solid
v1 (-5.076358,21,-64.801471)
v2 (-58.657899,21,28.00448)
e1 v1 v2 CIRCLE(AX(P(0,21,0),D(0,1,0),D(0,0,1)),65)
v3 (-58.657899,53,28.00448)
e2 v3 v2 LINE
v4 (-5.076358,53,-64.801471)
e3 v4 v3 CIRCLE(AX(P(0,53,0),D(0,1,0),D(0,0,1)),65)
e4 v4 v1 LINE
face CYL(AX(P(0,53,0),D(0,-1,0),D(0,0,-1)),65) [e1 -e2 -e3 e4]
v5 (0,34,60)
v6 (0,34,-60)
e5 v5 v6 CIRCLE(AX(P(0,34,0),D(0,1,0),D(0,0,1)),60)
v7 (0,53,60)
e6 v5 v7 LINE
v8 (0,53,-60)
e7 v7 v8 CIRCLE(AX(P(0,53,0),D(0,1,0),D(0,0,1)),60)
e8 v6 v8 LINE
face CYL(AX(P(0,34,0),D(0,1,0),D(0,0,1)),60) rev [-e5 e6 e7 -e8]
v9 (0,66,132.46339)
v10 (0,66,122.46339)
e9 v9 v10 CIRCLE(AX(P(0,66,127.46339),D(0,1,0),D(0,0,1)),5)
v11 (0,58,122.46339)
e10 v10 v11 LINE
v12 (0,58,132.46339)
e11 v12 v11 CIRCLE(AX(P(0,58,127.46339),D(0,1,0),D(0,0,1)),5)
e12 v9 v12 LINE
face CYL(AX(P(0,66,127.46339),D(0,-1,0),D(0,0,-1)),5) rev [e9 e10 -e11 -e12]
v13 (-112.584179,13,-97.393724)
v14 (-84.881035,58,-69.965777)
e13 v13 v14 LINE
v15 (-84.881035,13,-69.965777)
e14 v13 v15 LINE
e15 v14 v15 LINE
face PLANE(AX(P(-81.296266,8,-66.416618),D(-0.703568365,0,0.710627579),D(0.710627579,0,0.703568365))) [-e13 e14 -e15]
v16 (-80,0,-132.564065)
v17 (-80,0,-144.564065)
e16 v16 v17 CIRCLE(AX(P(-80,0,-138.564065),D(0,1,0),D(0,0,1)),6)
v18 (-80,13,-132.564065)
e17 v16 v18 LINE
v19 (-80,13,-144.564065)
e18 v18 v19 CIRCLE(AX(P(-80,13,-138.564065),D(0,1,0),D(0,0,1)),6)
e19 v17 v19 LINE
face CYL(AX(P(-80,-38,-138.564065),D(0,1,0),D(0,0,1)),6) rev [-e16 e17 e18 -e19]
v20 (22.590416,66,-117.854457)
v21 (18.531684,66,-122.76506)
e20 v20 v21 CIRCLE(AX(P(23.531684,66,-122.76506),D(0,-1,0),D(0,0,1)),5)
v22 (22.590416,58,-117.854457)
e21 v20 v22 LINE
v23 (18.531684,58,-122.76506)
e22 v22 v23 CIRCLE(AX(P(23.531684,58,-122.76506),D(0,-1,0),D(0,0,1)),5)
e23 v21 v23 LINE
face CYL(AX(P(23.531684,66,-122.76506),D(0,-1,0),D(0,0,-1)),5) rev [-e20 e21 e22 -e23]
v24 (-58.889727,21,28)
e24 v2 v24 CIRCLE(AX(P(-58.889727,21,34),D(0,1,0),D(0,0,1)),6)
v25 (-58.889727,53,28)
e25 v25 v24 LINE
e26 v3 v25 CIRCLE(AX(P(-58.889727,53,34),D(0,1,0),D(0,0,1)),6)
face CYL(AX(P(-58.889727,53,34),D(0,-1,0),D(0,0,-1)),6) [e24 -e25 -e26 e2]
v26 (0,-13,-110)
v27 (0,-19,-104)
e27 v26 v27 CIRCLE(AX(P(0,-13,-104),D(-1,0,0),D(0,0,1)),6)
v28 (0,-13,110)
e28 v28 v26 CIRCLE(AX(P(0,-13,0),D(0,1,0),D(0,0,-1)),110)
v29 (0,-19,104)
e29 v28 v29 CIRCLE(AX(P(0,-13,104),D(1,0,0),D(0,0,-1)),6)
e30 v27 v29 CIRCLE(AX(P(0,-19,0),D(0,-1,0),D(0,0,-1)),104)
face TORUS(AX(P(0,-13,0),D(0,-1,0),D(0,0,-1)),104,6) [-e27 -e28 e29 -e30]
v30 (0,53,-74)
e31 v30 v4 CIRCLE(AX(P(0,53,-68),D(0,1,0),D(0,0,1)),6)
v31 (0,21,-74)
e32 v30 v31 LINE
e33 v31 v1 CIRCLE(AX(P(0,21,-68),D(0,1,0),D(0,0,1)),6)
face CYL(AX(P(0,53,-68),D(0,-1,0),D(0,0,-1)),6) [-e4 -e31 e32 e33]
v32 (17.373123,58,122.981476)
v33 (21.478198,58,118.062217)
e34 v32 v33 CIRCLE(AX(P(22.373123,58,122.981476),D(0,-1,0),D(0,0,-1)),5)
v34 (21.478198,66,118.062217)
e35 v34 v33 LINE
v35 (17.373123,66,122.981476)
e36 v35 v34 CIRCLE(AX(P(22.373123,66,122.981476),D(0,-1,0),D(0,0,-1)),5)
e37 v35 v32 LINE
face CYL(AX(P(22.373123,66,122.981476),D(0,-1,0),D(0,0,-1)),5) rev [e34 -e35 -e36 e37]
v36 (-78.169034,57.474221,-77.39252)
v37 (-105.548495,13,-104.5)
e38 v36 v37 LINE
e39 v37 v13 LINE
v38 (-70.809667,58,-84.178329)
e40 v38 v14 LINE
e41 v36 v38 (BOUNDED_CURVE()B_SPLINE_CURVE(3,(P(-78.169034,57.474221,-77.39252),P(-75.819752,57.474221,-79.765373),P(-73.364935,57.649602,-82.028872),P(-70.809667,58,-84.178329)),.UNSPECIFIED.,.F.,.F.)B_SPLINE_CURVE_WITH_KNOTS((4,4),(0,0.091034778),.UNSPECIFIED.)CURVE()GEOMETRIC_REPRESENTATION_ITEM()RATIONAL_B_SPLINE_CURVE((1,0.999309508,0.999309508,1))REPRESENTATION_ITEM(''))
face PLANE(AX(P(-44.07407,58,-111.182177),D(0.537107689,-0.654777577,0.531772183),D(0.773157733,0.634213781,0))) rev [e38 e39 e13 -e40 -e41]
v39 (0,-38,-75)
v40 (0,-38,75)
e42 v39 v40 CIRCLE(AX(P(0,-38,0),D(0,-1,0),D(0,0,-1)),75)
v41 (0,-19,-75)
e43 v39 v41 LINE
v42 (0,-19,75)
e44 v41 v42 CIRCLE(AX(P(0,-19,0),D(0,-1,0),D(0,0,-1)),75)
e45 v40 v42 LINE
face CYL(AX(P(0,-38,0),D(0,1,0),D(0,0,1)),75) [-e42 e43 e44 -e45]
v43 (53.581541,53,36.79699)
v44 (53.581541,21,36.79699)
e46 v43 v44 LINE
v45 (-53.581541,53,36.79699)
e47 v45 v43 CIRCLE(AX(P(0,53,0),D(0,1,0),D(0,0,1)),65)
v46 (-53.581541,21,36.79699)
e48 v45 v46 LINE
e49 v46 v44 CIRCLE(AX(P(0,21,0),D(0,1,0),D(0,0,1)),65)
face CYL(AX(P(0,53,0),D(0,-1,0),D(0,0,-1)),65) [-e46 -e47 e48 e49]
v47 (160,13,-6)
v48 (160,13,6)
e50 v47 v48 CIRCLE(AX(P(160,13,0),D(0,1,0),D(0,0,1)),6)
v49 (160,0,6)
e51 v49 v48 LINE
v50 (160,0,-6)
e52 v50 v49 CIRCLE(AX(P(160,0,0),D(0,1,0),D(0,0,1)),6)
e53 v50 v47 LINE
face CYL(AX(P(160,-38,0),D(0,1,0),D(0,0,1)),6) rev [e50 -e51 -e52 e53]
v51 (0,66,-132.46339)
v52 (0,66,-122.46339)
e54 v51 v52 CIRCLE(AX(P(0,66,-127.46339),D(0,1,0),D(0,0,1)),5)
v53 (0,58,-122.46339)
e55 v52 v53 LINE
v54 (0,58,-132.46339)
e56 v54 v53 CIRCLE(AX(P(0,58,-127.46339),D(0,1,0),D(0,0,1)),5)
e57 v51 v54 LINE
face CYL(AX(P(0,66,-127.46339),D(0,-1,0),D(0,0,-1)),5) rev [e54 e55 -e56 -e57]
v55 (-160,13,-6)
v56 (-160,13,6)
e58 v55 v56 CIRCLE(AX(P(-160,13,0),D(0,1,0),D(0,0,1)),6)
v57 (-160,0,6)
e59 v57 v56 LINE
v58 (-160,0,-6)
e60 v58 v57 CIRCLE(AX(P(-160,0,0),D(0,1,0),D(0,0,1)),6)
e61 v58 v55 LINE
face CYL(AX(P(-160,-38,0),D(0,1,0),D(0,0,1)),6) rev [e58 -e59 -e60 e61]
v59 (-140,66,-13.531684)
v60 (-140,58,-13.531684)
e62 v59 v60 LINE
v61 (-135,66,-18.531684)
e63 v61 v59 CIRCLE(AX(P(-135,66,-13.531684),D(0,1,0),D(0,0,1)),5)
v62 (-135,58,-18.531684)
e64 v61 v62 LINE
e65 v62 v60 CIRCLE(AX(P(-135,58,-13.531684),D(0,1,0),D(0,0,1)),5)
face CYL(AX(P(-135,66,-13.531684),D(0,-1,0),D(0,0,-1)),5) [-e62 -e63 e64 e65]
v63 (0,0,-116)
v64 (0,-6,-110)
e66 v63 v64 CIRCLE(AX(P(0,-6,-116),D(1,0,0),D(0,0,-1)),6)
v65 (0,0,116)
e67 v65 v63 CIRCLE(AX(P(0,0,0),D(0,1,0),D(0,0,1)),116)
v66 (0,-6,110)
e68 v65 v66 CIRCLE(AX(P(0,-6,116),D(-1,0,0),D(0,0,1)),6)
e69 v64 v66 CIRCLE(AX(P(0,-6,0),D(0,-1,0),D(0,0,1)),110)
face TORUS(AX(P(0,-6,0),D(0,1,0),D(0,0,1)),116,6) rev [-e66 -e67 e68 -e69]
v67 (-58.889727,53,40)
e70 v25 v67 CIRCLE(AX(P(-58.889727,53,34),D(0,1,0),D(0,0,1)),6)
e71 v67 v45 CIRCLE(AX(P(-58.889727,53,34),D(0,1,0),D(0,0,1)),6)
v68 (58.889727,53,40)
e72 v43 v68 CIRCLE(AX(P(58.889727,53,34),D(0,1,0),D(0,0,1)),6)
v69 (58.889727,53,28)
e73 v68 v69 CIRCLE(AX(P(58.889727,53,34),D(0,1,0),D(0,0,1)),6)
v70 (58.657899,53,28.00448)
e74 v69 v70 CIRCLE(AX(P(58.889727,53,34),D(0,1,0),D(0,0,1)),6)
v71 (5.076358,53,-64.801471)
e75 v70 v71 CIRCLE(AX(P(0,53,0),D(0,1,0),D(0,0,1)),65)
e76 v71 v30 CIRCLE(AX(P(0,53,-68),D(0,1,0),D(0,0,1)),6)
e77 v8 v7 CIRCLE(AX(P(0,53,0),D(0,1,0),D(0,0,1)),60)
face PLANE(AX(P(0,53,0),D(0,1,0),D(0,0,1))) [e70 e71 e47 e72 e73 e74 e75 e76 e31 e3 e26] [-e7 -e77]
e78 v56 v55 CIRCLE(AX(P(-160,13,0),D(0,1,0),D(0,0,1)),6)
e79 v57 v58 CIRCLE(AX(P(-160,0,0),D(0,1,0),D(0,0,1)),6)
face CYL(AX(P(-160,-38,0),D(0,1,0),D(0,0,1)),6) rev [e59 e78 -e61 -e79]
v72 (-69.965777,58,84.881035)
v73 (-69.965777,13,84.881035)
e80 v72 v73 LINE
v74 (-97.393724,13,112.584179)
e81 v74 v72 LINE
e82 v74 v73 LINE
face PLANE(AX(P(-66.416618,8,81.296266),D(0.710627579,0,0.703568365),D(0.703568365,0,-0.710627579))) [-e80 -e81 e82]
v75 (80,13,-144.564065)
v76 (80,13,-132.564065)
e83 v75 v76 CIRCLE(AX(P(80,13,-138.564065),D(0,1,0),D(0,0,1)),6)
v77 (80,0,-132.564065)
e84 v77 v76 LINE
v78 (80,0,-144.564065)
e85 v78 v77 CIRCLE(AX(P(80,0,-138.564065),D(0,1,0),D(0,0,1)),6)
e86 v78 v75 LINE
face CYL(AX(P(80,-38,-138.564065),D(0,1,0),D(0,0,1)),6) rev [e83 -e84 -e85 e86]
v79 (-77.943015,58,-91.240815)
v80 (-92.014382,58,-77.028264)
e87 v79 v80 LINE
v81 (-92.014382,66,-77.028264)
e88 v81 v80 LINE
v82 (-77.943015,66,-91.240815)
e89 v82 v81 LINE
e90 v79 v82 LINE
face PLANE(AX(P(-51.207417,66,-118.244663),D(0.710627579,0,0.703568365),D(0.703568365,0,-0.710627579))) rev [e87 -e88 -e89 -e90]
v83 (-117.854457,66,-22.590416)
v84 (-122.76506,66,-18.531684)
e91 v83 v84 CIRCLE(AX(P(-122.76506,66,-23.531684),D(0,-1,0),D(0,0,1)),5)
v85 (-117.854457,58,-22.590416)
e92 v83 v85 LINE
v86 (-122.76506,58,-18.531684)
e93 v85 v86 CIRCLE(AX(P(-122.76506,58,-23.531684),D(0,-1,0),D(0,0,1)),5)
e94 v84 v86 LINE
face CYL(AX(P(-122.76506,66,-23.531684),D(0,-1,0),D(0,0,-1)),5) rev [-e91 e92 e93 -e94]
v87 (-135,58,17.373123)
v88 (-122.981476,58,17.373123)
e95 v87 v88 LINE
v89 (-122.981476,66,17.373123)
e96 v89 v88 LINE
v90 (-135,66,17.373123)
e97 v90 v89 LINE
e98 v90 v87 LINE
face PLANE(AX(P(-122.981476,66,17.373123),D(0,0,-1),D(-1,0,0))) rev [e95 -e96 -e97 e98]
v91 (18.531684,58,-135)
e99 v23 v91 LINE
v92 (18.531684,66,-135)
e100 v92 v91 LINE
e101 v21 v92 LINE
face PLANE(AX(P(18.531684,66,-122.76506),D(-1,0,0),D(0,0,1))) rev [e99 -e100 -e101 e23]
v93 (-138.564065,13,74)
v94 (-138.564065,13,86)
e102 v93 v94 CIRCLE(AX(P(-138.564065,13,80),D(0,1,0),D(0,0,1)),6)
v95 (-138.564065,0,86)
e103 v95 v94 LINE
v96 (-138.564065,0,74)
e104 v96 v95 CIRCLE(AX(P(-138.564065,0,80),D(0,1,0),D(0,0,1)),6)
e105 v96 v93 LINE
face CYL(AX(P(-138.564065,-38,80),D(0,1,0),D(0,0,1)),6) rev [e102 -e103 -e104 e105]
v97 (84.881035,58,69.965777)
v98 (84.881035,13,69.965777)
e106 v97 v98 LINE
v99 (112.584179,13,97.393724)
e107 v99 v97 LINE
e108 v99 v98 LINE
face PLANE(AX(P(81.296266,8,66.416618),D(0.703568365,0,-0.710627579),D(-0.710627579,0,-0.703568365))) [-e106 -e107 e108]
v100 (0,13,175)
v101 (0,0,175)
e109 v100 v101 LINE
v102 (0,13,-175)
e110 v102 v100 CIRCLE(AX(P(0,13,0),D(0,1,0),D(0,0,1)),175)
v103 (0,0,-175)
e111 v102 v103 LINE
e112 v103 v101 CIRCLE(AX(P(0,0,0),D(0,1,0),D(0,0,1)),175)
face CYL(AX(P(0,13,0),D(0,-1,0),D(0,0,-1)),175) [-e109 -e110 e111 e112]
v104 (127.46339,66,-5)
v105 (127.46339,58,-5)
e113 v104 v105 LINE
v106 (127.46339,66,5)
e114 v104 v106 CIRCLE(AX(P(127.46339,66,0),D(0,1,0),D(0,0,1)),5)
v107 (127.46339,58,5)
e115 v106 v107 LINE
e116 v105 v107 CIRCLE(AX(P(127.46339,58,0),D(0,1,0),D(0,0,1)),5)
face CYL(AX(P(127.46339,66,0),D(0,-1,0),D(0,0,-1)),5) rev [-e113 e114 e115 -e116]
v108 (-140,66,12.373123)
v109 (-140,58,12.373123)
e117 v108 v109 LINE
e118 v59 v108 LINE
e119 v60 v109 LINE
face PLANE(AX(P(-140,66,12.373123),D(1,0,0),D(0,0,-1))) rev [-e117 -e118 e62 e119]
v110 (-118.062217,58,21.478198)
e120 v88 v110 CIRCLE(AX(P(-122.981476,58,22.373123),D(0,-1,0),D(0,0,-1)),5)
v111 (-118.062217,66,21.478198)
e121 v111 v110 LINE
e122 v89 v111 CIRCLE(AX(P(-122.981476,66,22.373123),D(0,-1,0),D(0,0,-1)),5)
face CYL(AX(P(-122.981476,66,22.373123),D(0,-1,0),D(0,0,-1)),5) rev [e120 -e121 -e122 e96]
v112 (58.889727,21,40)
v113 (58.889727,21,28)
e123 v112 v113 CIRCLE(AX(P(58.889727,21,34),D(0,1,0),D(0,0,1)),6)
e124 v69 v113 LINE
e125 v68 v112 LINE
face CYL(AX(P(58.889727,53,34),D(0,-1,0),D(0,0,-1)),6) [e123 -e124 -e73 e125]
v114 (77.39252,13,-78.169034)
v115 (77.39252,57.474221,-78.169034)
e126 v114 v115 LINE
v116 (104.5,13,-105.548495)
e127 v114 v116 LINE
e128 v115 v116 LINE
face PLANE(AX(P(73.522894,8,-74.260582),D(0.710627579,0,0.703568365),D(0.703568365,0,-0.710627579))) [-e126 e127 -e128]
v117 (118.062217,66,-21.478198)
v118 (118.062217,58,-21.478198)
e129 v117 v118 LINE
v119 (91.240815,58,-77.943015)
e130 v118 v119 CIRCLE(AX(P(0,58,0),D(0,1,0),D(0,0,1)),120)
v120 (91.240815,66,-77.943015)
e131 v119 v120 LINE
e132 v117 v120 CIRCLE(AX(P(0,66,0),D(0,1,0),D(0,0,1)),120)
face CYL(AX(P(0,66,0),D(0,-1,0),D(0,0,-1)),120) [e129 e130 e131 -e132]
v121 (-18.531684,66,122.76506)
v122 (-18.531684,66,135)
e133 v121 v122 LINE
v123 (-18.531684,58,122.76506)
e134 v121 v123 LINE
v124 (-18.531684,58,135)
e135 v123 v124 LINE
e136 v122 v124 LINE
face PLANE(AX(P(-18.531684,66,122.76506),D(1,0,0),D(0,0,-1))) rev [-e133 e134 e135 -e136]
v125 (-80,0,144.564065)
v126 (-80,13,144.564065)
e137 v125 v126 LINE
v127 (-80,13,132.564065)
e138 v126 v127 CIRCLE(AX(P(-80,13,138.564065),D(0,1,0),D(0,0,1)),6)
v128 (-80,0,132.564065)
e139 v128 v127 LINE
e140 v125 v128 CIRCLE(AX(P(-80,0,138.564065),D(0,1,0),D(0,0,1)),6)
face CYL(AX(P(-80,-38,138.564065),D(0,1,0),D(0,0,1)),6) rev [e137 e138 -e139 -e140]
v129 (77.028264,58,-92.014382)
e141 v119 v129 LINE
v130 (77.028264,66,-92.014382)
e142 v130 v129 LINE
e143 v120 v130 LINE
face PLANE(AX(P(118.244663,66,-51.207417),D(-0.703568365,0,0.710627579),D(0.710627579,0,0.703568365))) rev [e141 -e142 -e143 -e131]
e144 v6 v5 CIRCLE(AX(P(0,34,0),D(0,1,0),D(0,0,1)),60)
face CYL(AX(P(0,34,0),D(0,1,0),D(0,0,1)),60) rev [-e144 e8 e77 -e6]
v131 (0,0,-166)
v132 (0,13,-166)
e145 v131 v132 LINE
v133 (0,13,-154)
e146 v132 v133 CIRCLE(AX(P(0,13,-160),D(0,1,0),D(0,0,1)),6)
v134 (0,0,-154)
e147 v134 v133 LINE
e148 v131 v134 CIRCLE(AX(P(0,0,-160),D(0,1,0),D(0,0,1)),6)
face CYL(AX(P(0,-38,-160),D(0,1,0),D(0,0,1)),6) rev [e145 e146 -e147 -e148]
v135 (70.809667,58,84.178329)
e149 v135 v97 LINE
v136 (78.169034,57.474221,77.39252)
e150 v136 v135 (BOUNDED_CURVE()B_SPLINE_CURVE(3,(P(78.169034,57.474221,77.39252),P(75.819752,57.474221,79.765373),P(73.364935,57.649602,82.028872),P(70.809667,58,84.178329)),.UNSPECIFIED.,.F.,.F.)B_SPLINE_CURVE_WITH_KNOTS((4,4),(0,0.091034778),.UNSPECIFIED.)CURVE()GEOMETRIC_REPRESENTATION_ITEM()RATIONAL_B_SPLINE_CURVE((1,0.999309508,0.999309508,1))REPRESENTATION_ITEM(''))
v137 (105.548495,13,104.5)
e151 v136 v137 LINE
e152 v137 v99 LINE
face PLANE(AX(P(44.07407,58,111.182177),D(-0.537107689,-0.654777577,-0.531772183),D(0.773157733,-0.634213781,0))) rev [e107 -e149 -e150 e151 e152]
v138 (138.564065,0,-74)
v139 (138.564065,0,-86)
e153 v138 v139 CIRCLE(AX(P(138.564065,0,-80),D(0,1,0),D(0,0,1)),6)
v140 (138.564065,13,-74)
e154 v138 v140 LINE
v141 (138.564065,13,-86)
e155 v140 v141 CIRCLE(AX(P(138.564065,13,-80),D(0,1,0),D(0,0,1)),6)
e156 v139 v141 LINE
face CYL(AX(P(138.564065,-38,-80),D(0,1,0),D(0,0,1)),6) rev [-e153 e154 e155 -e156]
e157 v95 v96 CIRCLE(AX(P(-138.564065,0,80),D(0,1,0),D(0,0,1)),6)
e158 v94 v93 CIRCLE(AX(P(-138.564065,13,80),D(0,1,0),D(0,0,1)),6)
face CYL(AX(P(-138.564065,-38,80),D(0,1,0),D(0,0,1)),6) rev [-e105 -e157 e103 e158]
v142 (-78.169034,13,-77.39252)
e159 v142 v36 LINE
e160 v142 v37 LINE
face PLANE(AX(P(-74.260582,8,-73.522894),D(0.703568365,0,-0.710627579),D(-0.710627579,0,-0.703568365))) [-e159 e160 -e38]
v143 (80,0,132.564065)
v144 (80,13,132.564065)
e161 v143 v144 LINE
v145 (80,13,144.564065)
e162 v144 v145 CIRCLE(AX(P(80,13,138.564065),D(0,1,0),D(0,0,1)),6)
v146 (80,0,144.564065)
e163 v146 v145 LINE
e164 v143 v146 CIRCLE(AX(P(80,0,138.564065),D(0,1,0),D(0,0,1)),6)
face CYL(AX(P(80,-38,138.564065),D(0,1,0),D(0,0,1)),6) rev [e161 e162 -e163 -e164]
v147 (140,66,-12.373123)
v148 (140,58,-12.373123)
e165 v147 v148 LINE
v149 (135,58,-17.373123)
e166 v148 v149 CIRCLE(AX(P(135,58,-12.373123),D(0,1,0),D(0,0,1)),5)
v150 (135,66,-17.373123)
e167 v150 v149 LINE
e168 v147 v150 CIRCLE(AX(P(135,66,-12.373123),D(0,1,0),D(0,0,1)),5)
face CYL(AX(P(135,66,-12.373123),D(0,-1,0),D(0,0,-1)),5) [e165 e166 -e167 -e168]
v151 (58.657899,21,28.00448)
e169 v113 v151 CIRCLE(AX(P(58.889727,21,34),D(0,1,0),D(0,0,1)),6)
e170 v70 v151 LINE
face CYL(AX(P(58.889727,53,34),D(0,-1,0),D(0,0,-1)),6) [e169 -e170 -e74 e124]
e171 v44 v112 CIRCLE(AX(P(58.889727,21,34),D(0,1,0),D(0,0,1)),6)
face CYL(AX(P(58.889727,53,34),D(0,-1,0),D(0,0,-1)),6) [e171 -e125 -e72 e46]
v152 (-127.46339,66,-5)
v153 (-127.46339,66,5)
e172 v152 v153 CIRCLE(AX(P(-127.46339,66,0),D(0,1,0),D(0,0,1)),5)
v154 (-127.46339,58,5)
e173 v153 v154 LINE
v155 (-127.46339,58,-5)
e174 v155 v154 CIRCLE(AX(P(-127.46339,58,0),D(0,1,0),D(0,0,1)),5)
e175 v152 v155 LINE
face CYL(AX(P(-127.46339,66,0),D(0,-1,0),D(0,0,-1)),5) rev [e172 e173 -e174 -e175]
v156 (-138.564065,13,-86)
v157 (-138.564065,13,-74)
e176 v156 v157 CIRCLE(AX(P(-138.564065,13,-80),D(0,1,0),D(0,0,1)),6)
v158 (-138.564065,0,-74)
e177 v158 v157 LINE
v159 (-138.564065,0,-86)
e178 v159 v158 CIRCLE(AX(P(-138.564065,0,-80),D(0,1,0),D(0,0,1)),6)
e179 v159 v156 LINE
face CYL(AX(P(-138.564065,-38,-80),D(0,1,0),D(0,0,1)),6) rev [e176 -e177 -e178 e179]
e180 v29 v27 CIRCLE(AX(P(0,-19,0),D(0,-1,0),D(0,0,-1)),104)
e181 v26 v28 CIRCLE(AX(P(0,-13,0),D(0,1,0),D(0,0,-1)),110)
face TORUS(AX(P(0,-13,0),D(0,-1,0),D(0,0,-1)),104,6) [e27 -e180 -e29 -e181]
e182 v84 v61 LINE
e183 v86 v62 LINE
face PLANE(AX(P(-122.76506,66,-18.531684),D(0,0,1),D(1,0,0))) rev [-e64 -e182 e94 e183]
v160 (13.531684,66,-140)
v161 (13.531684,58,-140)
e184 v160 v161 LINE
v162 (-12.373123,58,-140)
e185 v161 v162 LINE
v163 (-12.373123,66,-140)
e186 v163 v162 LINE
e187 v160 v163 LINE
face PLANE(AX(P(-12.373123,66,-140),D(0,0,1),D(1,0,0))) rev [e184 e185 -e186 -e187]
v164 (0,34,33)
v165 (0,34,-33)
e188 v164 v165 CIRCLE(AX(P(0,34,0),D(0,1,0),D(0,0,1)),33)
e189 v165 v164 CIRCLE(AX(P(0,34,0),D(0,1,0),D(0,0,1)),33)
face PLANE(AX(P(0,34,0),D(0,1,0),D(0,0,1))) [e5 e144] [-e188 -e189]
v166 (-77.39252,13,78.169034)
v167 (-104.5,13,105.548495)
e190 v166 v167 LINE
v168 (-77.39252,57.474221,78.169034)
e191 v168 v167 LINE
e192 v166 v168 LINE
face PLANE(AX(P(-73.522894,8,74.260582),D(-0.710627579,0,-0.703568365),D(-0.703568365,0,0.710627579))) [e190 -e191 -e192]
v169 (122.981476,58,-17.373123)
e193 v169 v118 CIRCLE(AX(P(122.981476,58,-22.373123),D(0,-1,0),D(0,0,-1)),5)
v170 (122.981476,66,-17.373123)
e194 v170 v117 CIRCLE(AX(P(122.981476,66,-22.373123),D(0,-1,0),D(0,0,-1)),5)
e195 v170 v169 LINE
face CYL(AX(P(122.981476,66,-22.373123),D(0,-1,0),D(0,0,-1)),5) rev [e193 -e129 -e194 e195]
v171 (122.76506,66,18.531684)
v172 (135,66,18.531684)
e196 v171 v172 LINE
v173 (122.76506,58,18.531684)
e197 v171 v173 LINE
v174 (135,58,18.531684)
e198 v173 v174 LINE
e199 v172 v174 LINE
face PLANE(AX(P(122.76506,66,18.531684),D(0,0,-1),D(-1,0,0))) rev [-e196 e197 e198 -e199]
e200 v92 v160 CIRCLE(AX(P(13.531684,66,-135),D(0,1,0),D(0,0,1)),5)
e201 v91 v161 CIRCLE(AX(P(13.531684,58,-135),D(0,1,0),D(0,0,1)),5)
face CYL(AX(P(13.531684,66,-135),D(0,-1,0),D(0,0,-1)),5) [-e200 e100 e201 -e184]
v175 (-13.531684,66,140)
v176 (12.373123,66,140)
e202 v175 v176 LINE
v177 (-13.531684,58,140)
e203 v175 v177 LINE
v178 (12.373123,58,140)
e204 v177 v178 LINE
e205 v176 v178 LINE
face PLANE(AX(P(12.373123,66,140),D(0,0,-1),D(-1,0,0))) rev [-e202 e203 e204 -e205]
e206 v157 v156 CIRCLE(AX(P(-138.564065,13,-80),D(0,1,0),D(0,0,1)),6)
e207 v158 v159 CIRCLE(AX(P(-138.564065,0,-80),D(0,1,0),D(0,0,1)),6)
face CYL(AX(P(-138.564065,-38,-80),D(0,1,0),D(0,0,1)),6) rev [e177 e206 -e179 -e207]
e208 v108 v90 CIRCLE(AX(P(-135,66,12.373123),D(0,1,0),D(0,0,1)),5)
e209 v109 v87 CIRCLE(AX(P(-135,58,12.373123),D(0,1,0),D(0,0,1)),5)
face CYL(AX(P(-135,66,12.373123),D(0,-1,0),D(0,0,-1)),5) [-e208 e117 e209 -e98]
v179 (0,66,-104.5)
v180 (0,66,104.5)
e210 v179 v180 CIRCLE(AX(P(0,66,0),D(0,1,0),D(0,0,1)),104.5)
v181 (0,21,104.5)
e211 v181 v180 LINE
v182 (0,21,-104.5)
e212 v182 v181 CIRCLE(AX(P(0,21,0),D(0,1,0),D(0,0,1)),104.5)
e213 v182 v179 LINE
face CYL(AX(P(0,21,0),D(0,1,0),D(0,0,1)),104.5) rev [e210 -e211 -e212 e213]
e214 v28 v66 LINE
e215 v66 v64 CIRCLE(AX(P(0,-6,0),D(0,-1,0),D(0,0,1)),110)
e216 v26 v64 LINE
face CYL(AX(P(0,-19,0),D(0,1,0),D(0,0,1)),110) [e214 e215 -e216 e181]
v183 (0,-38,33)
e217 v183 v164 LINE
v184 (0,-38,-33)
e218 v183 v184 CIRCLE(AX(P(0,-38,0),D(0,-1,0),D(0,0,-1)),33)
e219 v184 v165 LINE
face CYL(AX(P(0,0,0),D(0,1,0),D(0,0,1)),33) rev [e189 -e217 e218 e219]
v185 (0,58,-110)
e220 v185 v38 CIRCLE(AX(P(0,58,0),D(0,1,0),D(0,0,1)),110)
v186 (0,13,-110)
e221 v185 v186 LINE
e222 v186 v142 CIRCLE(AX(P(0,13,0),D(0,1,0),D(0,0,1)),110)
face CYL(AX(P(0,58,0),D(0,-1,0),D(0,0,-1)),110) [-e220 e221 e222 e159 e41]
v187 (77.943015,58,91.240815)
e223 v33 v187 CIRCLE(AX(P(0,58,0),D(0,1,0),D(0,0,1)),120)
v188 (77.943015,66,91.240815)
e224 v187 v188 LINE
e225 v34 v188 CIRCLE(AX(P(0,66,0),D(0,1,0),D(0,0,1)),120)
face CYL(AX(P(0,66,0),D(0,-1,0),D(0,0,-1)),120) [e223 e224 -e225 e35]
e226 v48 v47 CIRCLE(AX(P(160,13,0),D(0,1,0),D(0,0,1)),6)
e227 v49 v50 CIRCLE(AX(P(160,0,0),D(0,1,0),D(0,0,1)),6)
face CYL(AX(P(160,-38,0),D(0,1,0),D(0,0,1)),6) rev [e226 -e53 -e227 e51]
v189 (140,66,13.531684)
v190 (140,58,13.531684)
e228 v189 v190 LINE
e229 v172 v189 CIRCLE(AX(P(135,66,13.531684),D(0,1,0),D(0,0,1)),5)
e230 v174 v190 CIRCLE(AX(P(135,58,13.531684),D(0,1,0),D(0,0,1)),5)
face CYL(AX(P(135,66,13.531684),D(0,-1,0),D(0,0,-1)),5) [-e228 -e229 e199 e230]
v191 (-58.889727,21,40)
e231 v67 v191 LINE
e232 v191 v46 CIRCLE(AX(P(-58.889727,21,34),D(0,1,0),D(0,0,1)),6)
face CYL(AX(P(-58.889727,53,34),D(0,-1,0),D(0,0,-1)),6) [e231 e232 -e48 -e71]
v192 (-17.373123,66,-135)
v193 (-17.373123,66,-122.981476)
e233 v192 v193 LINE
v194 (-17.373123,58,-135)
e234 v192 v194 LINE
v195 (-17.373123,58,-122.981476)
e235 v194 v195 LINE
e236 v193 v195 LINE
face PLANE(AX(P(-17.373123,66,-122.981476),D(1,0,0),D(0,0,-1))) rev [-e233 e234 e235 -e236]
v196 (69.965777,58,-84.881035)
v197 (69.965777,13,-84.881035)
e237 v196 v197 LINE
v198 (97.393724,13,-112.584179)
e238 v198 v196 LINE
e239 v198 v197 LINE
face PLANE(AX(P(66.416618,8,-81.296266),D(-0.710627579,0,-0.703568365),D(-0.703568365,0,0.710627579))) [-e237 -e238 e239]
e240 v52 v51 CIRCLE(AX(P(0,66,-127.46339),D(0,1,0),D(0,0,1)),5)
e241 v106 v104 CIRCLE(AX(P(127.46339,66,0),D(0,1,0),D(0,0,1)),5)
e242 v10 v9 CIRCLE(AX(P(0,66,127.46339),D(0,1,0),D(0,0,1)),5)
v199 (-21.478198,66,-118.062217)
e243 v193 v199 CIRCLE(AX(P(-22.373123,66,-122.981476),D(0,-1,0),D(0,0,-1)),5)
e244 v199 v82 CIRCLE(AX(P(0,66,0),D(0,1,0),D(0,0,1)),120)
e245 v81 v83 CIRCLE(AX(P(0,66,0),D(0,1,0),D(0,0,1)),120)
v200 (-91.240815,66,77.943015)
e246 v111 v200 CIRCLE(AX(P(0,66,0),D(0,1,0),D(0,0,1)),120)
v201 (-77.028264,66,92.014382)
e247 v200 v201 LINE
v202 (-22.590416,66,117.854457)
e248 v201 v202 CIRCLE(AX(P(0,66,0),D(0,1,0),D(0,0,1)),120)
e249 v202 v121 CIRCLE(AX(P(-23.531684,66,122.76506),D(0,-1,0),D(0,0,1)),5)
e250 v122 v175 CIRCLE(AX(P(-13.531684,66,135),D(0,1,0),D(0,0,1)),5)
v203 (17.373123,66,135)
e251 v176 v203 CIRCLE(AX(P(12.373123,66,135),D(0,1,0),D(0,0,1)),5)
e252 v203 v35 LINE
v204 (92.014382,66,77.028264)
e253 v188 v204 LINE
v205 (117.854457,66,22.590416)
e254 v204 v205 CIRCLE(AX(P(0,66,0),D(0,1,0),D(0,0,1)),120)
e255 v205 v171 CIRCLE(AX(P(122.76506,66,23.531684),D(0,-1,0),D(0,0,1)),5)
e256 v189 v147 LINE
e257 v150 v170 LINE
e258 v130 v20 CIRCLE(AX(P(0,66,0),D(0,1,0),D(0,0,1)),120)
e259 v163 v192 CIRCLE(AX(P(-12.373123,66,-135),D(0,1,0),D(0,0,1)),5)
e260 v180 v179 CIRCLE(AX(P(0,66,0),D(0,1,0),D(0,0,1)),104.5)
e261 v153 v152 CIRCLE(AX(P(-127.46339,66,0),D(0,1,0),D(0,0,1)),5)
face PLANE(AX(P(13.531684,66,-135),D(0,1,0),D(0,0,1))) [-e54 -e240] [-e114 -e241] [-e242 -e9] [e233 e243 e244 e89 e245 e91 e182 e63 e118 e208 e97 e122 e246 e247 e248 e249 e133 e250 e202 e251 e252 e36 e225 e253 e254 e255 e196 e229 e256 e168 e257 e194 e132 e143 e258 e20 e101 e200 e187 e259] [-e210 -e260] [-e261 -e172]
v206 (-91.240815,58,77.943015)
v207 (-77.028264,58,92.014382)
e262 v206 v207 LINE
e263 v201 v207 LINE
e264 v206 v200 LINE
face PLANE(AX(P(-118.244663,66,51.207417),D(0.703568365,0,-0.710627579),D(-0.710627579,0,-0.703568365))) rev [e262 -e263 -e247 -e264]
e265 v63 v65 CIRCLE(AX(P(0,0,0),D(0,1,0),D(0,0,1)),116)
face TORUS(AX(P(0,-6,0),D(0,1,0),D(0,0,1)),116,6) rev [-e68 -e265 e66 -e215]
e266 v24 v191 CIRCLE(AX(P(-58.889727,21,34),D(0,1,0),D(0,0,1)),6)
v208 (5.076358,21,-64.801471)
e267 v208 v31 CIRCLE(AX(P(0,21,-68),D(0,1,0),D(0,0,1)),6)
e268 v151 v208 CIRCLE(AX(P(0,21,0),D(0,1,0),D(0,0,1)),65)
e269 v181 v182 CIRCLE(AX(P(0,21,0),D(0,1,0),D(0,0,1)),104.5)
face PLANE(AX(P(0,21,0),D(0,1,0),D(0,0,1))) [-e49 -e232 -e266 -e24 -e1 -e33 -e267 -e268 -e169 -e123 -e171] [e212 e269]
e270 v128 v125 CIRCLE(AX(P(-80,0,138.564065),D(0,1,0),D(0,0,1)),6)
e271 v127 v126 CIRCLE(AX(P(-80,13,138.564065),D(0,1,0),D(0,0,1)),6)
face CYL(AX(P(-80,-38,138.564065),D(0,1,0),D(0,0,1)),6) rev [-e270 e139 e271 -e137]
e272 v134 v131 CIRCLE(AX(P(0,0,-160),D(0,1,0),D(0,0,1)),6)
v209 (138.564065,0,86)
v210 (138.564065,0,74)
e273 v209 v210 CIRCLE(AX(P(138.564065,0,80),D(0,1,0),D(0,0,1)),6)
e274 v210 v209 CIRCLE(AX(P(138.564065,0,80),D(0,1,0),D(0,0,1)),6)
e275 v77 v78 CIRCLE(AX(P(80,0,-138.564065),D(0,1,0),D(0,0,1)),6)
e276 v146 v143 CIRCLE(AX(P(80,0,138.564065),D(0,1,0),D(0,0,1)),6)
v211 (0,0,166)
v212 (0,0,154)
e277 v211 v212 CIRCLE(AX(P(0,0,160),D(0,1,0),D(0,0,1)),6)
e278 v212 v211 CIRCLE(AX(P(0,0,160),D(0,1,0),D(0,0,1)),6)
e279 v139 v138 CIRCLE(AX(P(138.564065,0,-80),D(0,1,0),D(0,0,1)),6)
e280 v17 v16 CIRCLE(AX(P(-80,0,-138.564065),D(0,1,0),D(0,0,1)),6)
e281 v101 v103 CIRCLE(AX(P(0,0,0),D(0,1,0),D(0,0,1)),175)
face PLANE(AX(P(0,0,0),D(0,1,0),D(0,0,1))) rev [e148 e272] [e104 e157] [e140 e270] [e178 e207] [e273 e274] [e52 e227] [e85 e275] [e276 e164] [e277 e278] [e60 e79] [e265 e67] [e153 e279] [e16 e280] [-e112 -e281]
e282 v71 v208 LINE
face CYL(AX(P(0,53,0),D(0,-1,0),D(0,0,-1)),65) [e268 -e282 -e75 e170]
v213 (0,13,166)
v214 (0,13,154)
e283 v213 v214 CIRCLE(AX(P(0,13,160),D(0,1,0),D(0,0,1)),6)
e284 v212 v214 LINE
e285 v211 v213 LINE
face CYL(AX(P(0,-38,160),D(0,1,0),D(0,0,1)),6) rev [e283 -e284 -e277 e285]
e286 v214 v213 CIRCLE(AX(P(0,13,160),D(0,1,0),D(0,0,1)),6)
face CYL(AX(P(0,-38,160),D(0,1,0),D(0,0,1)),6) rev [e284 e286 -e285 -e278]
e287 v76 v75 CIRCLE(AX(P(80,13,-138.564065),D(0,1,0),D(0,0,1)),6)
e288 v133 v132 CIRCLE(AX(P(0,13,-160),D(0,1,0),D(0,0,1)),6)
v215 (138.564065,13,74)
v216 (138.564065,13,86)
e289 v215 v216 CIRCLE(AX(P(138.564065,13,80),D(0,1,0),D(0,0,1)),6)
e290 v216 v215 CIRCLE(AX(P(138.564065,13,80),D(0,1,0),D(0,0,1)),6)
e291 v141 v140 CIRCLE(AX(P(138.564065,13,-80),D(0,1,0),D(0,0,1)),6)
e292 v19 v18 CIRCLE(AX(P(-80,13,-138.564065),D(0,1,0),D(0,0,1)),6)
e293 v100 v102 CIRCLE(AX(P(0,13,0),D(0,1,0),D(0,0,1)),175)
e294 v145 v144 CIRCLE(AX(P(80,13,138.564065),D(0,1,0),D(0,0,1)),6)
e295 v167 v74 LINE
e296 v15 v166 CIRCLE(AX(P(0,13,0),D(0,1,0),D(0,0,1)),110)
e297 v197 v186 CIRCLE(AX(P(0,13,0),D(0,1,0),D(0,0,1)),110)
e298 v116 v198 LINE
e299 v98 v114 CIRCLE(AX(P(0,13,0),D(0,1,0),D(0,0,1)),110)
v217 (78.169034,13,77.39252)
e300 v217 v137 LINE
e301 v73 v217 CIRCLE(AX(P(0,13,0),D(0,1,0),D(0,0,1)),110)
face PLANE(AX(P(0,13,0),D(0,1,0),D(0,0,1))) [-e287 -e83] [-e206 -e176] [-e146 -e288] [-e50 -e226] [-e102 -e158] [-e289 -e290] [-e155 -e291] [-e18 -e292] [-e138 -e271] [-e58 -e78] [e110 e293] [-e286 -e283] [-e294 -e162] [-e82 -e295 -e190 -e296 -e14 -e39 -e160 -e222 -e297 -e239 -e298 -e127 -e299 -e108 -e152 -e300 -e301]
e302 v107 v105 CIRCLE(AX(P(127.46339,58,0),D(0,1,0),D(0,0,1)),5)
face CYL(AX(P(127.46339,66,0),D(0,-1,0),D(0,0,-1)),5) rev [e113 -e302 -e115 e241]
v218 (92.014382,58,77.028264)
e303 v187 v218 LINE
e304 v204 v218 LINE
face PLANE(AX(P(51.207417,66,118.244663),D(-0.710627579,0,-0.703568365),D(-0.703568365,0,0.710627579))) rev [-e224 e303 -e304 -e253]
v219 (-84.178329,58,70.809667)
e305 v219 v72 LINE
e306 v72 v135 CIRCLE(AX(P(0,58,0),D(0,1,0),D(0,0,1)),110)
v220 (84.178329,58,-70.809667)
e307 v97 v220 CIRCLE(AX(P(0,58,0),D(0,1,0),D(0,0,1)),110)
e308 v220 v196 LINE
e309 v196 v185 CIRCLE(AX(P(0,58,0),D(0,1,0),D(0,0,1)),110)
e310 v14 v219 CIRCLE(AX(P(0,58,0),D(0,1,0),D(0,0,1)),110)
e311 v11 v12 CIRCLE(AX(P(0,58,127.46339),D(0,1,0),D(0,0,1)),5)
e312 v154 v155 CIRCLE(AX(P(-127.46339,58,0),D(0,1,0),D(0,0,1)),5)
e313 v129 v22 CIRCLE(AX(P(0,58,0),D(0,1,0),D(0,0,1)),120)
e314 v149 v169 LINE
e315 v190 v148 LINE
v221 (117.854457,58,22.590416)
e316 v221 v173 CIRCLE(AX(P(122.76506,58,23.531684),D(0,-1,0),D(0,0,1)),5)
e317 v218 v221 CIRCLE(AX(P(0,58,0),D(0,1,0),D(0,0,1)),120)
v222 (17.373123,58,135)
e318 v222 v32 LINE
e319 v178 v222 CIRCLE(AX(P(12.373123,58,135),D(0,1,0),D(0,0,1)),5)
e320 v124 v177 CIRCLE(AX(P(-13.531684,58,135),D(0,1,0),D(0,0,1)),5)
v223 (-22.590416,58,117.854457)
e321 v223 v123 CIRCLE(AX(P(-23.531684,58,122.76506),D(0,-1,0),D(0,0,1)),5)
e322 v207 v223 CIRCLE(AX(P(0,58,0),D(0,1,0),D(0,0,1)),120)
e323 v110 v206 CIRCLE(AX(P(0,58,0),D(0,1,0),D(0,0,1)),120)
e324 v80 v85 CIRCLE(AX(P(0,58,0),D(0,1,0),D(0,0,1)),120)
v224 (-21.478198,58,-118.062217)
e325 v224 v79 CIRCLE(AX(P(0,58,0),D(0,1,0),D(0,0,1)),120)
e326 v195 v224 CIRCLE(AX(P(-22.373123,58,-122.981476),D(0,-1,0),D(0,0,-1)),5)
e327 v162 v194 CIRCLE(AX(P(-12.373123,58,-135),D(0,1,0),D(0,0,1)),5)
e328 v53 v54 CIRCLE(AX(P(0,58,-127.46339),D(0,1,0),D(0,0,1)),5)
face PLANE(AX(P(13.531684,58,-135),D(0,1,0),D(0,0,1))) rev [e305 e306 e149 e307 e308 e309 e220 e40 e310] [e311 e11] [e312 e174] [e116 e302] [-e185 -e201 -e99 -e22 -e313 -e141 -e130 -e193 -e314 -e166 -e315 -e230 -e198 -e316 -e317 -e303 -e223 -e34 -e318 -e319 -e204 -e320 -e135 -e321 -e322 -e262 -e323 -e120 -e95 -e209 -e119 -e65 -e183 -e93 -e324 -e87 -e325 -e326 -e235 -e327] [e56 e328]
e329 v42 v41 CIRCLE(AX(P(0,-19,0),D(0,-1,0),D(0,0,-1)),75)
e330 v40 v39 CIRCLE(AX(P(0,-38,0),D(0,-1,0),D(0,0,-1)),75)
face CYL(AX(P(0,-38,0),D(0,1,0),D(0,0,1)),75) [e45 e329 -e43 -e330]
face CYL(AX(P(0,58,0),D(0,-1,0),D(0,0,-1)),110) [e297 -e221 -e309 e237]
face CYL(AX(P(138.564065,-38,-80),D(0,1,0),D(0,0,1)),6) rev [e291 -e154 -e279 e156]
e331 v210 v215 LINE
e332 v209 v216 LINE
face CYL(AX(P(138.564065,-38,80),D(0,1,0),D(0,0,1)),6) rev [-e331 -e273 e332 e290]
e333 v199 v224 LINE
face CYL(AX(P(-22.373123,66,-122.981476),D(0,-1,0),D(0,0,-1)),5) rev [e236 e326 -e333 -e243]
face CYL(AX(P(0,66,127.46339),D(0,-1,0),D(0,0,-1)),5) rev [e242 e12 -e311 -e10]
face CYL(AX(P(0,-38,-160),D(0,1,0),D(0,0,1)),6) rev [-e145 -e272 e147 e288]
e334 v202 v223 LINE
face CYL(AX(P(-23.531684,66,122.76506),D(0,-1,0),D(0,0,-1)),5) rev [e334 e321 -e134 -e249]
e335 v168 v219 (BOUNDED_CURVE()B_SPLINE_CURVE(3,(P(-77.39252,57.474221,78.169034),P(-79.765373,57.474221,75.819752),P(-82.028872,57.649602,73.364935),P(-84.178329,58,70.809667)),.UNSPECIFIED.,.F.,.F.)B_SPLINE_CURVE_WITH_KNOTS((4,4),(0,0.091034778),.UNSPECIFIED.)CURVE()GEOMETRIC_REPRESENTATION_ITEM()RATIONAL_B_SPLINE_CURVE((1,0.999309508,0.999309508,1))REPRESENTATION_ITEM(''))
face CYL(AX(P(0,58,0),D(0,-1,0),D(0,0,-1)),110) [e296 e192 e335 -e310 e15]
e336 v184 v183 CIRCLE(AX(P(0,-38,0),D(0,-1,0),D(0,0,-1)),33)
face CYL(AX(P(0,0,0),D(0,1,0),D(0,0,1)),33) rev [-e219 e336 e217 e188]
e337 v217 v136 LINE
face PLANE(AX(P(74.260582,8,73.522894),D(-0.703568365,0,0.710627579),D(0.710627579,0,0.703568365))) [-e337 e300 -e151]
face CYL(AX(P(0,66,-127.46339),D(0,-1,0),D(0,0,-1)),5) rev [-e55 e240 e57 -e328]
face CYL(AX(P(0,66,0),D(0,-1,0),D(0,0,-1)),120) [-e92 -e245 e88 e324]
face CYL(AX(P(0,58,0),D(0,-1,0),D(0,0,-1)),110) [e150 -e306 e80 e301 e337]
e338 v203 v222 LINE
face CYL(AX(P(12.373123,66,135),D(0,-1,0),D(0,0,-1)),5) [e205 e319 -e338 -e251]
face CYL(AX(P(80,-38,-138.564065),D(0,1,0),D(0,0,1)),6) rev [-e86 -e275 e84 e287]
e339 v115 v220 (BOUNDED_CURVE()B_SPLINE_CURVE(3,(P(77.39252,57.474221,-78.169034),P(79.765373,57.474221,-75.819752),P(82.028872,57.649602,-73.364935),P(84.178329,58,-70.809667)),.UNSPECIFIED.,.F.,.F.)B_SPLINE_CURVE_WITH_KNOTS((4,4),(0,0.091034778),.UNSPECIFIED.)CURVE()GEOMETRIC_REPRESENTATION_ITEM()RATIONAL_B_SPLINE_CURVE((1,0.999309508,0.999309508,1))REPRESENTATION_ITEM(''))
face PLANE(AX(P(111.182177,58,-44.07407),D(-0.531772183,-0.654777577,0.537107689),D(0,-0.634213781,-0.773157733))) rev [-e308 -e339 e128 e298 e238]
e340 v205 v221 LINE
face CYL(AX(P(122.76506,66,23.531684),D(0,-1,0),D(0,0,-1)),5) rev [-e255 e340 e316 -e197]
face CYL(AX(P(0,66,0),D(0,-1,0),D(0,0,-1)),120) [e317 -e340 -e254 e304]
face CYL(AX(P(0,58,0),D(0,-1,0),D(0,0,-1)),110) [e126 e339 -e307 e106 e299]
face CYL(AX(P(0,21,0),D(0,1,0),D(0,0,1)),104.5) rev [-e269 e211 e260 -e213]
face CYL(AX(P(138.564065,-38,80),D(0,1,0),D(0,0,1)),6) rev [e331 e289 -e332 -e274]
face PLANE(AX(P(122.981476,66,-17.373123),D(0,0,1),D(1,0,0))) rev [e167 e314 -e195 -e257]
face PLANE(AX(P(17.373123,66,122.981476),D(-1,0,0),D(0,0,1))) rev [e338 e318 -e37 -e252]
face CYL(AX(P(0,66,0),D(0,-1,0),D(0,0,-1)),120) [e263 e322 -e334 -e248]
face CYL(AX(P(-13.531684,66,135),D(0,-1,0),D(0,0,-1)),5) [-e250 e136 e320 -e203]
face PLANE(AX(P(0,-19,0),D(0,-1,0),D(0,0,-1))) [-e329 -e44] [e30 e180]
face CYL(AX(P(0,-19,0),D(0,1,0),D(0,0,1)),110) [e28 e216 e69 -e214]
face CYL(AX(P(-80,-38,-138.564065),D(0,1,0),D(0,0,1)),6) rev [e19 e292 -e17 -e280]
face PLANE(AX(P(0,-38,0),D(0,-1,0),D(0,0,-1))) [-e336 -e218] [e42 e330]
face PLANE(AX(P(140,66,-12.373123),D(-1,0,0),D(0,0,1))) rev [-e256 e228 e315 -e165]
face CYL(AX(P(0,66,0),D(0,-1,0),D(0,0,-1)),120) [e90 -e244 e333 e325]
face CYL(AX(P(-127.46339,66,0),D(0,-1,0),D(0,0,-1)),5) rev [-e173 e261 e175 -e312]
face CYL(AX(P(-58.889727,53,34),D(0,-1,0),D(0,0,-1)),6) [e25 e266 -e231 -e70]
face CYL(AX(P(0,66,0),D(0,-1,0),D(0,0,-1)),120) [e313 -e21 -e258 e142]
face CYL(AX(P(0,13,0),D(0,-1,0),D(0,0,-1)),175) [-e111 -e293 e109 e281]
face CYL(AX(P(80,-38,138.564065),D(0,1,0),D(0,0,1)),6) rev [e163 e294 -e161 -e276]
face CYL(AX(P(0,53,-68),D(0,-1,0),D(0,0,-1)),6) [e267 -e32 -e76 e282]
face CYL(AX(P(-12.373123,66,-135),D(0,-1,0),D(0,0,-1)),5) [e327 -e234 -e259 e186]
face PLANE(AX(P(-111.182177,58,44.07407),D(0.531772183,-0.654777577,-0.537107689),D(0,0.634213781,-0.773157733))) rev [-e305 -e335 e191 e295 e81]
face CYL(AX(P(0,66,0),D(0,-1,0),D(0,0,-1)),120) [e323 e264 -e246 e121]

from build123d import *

# Parameters (mm, degrees)
FLANGE_SKETCH_R                = 175
FLANGE_350X13_DEPTH            = 13
HUB_SKETCH_R                   = 110
HUB_220_DEPTH                  = 45
LUG_PLATE_SKETCH_R             = 5
MOUNTING_LUG_PLATE_DEPTH       = 8
HUB_BORE_SKETCH_R              = 104.5
HUB_BORE_209_DEPTH             = 45
BEARING_HOUSING_130_DEPTH      = 32
BEARING_SEAT_SKETCH_R          = 60
BEARING_SEAT_120_DEPTH         = 19
SHAFT_HOLE_SKETCH_R            = 33
SHAFT_HOLE_66_DEPTH            = 250.811929259
REAR_START                     = 19
REAR_BOSS_SKETCH_R             = 110
REAR_BOSS_220_DEPTH            = 19
REAR_STEP_SKETCH_R             = 75
REAR_STEP_150_DEPTH            = 19
REAR_SHAFT_HOLE_SKETCH_R       = 33
REAR_SHAFT_HOLE_66_DEPTH       = 269.451112868
FLANGE_BOLT_HOLES_SKETCH_R     = 6
FLANGE_BOLT_HOLES_12X_12_DEPTH = 254.09879494
REAR_BOSS_FILLET_R6_R          = 6
GUSSET_RIBS_4X_DEPTH           = 58
RIB_TRIM_CUT_1_DEPTH           = 58
RIB_TRIM_CUT_2_DEPTH           = 58
RIB_TRIM_CUT_3_DEPTH           = 58
RIB_TRIM_CUT_4_DEPTH           = 58


with BuildPart() as part:
    # Flange Sketch → Flange Ø350x13 (new body)
    with BuildSketch(Plane(origin=(0, 0, 0), x_dir=(1, 0, 0), z_dir=(0, 1, 0))):
        with Locations(Location((0, 0, 0), (0, 0, 90))):
            Circle(FLANGE_SKETCH_R)
    extrude(amount=FLANGE_350X13_DEPTH)

    # Hub Sketch → Hub Ø220 (add)
    with BuildSketch(Plane(origin=(0, 13, 0), x_dir=(1, 0, 0), z_dir=(0, 1, 0))):
        with Locations(Location((0, 0, 0), (0, 0, 90))):
            Circle(HUB_SKETCH_R)
    extrude(amount=HUB_220_DEPTH)

    # Lug Plate Sketch → Mounting Lug Plate (add)
    with BuildSketch(Plane(origin=(0, 58, 0), x_dir=(1, 0, 0), z_dir=(0, 1, 0))):
        with BuildLine():
            Line((122.981475637, 17.37312339), (135, 17.37312339))
            ThreePointArc((135, 17.37312339), (138.535533906, 15.908657296), (140, 12.37312339))
            Line((140, 12.37312339), (140, -13.53168384))
            ThreePointArc((140, -13.53168384), (138.535533906, -17.067217746), (135, -18.53168384))
            Line((135, -18.53168384), (122.765059588, -18.53168384))
            ThreePointArc((122.765059588, -18.53168384), (119.579650412, -19.677702991), (117.854457205, -22.590416486))
            ThreePointArc((117.854457205, -22.590416486), (84.451840643, -85.251900929), (21.478198454, -118.062216611))
            ThreePointArc((21.478198454, -118.062216611), (18.534202664, -119.777932651), (17.37312339, -122.981475637))
            Line((17.37312339, -122.981475637), (17.37312339, -135))
            ThreePointArc((17.37312339, -135), (15.908657296, -138.535533906), (12.37312339, -140))
            Line((12.37312339, -140), (-13.53168384, -140))
            ThreePointArc((-13.53168384, -140), (-17.067217746, -138.535533906), (-18.53168384, -135))
            Line((-18.53168384, -135), (-18.53168384, -122.765059588))
            ThreePointArc((-18.53168384, -122.765059588), (-19.677702991, -119.579650412), (-22.590416486, -117.854457205))
            ThreePointArc((-22.590416486, -117.854457205), (-85.251900929, -84.451840643), (-118.062216611, -21.478198454))
            ThreePointArc((-118.062216611, -21.478198454), (-119.777932651, -18.534202664), (-122.981475637, -17.37312339))
            Line((-122.981475637, -17.37312339), (-135, -17.37312339))
            ThreePointArc((-135, -17.37312339), (-138.535533906, -15.908657296), (-140, -12.37312339))
            Line((-140, -12.37312339), (-140, 13.53168384))
            ThreePointArc((-140, 13.53168384), (-138.535533906, 17.067217746), (-135, 18.53168384))
            Line((-135, 18.53168384), (-122.765059588, 18.53168384))
            ThreePointArc((-122.765059588, 18.53168384), (-119.579650412, 19.677702991), (-117.854457205, 22.590416486))
            ThreePointArc((-117.854457205, 22.590416486), (-84.451840643, 85.251900929), (-21.478198454, 118.062216611))
            ThreePointArc((-21.478198454, 118.062216611), (-18.534202664, 119.777932651), (-17.37312339, 122.981475637))
            Line((-17.37312339, 122.981475637), (-17.37312339, 135))
            ThreePointArc((-17.37312339, 135), (-15.908657296, 138.535533906), (-12.37312339, 140))
            Line((-12.37312339, 140), (13.53168384, 140))
            ThreePointArc((13.53168384, 140), (17.067217746, 138.535533906), (18.53168384, 135))
            Line((18.53168384, 135), (18.53168384, 122.765059588))
            ThreePointArc((18.53168384, 122.765059588), (19.677702991, 119.579650412), (22.590416486, 117.854457205))
            ThreePointArc((22.590416486, 117.854457205), (85.251900929, 84.451840643), (118.062216611, 21.478198454))
            ThreePointArc((118.062216611, 21.478198454), (119.777932651, 18.534202664), (122.981475637, 17.37312339))
        make_face()
        with Locations(Location((0, 127.463390021, 0), (0, 0, 270))):
            Circle(LUG_PLATE_SKETCH_R, mode=Mode.SUBTRACT)
        with Locations(Location((127.463390021, 0, 0), (0, 0, 270))):
            Circle(LUG_PLATE_SKETCH_R, mode=Mode.SUBTRACT)
        with Locations(Location((0, -127.463390021, 0), (0, 0, 270))):
            Circle(LUG_PLATE_SKETCH_R, mode=Mode.SUBTRACT)
        with Locations(Location((-127.463390021, 0, 0), (0, 0, 270))):
            Circle(LUG_PLATE_SKETCH_R, mode=Mode.SUBTRACT)
    extrude(amount=MOUNTING_LUG_PLATE_DEPTH)

    # Hub Bore Sketch → Hub Bore Ø209 (cut)
    with BuildSketch(Plane(origin=(0, 66, 0), x_dir=(1, 0, 0), z_dir=(0, 1, 0))):
        with Locations(Location((0, 0, 0), (0, 0, 270))):
            Circle(HUB_BORE_SKETCH_R)
    extrude(amount=-HUB_BORE_209_DEPTH, mode=Mode.SUBTRACT)

    # Bearing Housing Sketch → Bearing Housing Ø130 (add)
    with BuildSketch(Plane(origin=(0, 21, 0), x_dir=(1, 0, 0), z_dir=(0, 1, 0))):
        with BuildLine():
            ThreePointArc((-5.076357907, 64.801470588), (-56.291651246, 32.5), (-58.657898686, -28.004480388))
            ThreePointArc((-58.657898686, -28.004480388), (-64.08587988, -37), (-53.581540778, -36.7969902))
            ThreePointArc((-53.581540778, -36.7969902), (0, -65), (53.581540778, -36.7969902))
            ThreePointArc((53.581540778, -36.7969902), (64.08587988, -37), (58.657898686, -28.004480388))
            ThreePointArc((58.657898686, -28.004480388), (56.291651246, 32.5), (5.076357907, 64.801470588))
            ThreePointArc((5.076357907, 64.801470588), (0, 74), (-5.076357907, 64.801470588))
        make_face()
    extrude(amount=BEARING_HOUSING_130_DEPTH)

    # Bearing Seat Sketch → Bearing Seat Ø120 (cut)
    with BuildSketch(Plane(origin=(0, 53, 0), x_dir=(1, 0, 0), z_dir=(0, 1, 0))):
        with Locations(Location((0, 0, 0), (0, 0, 270))):
            Circle(BEARING_SEAT_SKETCH_R)
    extrude(amount=-BEARING_SEAT_120_DEPTH, mode=Mode.SUBTRACT)

    # Shaft Hole Sketch → Shaft Hole Ø66 (cut, through all)
    with BuildSketch(Plane(origin=(0, 34, 0), x_dir=(1, 0, 0), z_dir=(0, 1, 0))):
        with Locations(Location((0, 0, 0), (0, 0, 270))):
            Circle(SHAFT_HOLE_SKETCH_R)
    extrude(amount=-SHAFT_HOLE_66_DEPTH, mode=Mode.SUBTRACT)

    # Rear Boss Sketch → Rear Boss Ø220 (add)
    with BuildSketch(Plane.XZ.offset(REAR_START)):
        with Locations(Location((0, 0, 0), (0, 0, 270))):
            Circle(REAR_BOSS_SKETCH_R)
    extrude(amount=-REAR_BOSS_220_DEPTH)

    # Rear Step Sketch → Rear Step Ø150 (add)
    with BuildSketch(Plane.XZ.offset(19)):
        with Locations(Location((0, 0, 0), (0, 0, 270))):
            Circle(REAR_STEP_SKETCH_R)
    extrude(amount=REAR_STEP_150_DEPTH)

    # Rear Shaft Hole Sketch → Rear Shaft Hole Ø66 (cut, through all)
    with BuildSketch(Plane.XZ.offset(38)):
        with Locations(Location((0, 0, 0), (0, 0, 90))):
            Circle(REAR_SHAFT_HOLE_SKETCH_R)
    extrude(amount=-REAR_SHAFT_HOLE_66_DEPTH, mode=Mode.SUBTRACT)

    # Flange Bolt Holes Sketch → Flange Bolt Holes 12xØ12 (cut, through all)
    with BuildSketch(Plane(origin=(0, 13, 0), x_dir=(1, 0, 0), z_dir=(0, 1, 0))):
        with Locations(Location((0, 160, 0), (0, 0, 270))):
            Circle(FLANGE_BOLT_HOLES_SKETCH_R)
        with Locations(Location((80, 138.564064606, 0), (0, 0, 270))):
            Circle(FLANGE_BOLT_HOLES_SKETCH_R)
        with Locations(Location((138.564064606, 80, 0), (0, 0, 270))):
            Circle(FLANGE_BOLT_HOLES_SKETCH_R)
        with Locations(Location((160, 0, 0), (0, 0, 270))):
            Circle(FLANGE_BOLT_HOLES_SKETCH_R)
        with Locations(Location((138.564064606, -80, 0), (0, 0, 270))):
            Circle(FLANGE_BOLT_HOLES_SKETCH_R)
        with Locations(Location((80, -138.564064606, 0), (0, 0, 270))):
            Circle(FLANGE_BOLT_HOLES_SKETCH_R)
        with Locations(Location((0, -160, 0), (0, 0, 270))):
            Circle(FLANGE_BOLT_HOLES_SKETCH_R)
        with Locations(Location((-80, -138.564064606, 0), (0, 0, 270))):
            Circle(FLANGE_BOLT_HOLES_SKETCH_R)
        with Locations(Location((-138.564064605, -80, 0), (0, 0, 270))):
            Circle(FLANGE_BOLT_HOLES_SKETCH_R)
        with Locations(Location((-160, 0, 0), (0, 0, 270))):
            Circle(FLANGE_BOLT_HOLES_SKETCH_R)
        with Locations(Location((-138.564064606, 80, 0), (0, 0, 270))):
            Circle(FLANGE_BOLT_HOLES_SKETCH_R)
        with Locations(Location((-80, 138.564064606, 0), (0, 0, 270))):
            Circle(FLANGE_BOLT_HOLES_SKETCH_R)
    extrude(amount=-FLANGE_BOLT_HOLES_12X_12_DEPTH, mode=Mode.SUBTRACT)

    # Rear Boss Fillet R6
    rear_boss_fillet_r6_edges = [part.edges().sort_by_distance(p)[0] for p in [
        (0, 0, 110),
        (0, -19, 110),
    ]]
    fillet(rear_boss_fillet_r6_edges, radius=REAR_BOSS_FILLET_R6_R)

    # Gusset Ribs Sketch → Gusset Ribs 4x (add)
    with BuildSketch(Plane(origin=(0, 66, 0), x_dir=(1, 0, 0), z_dir=(0, 1, 0))):
        Polygon((-74.260582015, 73.522894114), (-105.548494983, 104.5), (-112.584178631, 97.393724209), (-81.296265662, 66.416618323), align=None)
        Polygon((104.5, 105.548494983), (97.393724209, 112.584178631), (66.416618323, 81.296265662), (73.522894114, 74.260582015), align=None)
        Polygon((105.548494983, -104.5), (112.584178631, -97.393724209), (81.296265662, -66.416618323), (74.260582015, -73.522894114), align=None)
        Polygon((-104.5, -105.548494983), (-97.393724209, -112.584178631), (-66.416618323, -81.296265662), (-73.522894114, -74.260582015), align=None)
    extrude(amount=-GUSSET_RIBS_4X_DEPTH)

    # Rib Trim Sketch 1 → Rib Trim Cut 1 (cut)
    with BuildSketch(Plane(origin=(7.106275791, 0, 7.035683647), x_dir=(0.7035683647248037, 0, -0.7106275790865887), z_dir=(0.7106275790865887, 0, 0.7035683647248037))):
        Polygon((-109.544511501, 58), (-148.52856558, 13), (-148.52856558, 66), (-119.582607431, 66), (-119.582607431, 58), align=None)
    extrude(amount=-RIB_TRIM_CUT_1_DEPTH, mode=Mode.SUBTRACT)

    # Rib Trim Sketch 2 → Rib Trim Cut 2 (cut)
    with BuildSketch(Plane(origin=(-7.035683647, 0, 7.106275791), x_dir=(0.7106275790865887, 0, 0.7035683647248037), z_dir=(-0.7035683647248037, 0, 0.7106275790865887))):
        Polygon((-109.544511501, 58), (-148.52856558, 13), (-148.52856558, 66), (-119.582607431, 66), (-119.582607431, 58), align=None)
    extrude(amount=-RIB_TRIM_CUT_2_DEPTH, mode=Mode.SUBTRACT)

    # Rib Trim Sketch 3 → Rib Trim Cut 3 (cut)
    with BuildSketch(Plane(origin=(-7.106275791, 0, -7.035683647), x_dir=(-0.7035683647248037, 0, 0.7106275790865887), z_dir=(-0.7106275790865887, 0, -0.7035683647248037))):
        Polygon((-109.544511501, 58), (-148.52856558, 13), (-148.52856558, 66), (-119.582607431, 66), (-119.582607431, 58), align=None)
    extrude(amount=-RIB_TRIM_CUT_3_DEPTH, mode=Mode.SUBTRACT)

    # Rib Trim Sketch 4 → Rib Trim Cut 4 (cut)
    with BuildSketch(Plane(origin=(7.035683647, 0, -7.106275791), x_dir=(-0.7106275790865887, 0, -0.7035683647248037), z_dir=(0.7035683647248037, 0, -0.7106275790865887))):
        Polygon((-109.544511501, 58), (-148.52856558, 13), (-148.52856558, 66), (-119.582607431, 66), (-119.582607431, 58), align=None)
    extrude(amount=-RIB_TRIM_CUT_4_DEPTH, mode=Mode.SUBTRACT)


solid = part.part
